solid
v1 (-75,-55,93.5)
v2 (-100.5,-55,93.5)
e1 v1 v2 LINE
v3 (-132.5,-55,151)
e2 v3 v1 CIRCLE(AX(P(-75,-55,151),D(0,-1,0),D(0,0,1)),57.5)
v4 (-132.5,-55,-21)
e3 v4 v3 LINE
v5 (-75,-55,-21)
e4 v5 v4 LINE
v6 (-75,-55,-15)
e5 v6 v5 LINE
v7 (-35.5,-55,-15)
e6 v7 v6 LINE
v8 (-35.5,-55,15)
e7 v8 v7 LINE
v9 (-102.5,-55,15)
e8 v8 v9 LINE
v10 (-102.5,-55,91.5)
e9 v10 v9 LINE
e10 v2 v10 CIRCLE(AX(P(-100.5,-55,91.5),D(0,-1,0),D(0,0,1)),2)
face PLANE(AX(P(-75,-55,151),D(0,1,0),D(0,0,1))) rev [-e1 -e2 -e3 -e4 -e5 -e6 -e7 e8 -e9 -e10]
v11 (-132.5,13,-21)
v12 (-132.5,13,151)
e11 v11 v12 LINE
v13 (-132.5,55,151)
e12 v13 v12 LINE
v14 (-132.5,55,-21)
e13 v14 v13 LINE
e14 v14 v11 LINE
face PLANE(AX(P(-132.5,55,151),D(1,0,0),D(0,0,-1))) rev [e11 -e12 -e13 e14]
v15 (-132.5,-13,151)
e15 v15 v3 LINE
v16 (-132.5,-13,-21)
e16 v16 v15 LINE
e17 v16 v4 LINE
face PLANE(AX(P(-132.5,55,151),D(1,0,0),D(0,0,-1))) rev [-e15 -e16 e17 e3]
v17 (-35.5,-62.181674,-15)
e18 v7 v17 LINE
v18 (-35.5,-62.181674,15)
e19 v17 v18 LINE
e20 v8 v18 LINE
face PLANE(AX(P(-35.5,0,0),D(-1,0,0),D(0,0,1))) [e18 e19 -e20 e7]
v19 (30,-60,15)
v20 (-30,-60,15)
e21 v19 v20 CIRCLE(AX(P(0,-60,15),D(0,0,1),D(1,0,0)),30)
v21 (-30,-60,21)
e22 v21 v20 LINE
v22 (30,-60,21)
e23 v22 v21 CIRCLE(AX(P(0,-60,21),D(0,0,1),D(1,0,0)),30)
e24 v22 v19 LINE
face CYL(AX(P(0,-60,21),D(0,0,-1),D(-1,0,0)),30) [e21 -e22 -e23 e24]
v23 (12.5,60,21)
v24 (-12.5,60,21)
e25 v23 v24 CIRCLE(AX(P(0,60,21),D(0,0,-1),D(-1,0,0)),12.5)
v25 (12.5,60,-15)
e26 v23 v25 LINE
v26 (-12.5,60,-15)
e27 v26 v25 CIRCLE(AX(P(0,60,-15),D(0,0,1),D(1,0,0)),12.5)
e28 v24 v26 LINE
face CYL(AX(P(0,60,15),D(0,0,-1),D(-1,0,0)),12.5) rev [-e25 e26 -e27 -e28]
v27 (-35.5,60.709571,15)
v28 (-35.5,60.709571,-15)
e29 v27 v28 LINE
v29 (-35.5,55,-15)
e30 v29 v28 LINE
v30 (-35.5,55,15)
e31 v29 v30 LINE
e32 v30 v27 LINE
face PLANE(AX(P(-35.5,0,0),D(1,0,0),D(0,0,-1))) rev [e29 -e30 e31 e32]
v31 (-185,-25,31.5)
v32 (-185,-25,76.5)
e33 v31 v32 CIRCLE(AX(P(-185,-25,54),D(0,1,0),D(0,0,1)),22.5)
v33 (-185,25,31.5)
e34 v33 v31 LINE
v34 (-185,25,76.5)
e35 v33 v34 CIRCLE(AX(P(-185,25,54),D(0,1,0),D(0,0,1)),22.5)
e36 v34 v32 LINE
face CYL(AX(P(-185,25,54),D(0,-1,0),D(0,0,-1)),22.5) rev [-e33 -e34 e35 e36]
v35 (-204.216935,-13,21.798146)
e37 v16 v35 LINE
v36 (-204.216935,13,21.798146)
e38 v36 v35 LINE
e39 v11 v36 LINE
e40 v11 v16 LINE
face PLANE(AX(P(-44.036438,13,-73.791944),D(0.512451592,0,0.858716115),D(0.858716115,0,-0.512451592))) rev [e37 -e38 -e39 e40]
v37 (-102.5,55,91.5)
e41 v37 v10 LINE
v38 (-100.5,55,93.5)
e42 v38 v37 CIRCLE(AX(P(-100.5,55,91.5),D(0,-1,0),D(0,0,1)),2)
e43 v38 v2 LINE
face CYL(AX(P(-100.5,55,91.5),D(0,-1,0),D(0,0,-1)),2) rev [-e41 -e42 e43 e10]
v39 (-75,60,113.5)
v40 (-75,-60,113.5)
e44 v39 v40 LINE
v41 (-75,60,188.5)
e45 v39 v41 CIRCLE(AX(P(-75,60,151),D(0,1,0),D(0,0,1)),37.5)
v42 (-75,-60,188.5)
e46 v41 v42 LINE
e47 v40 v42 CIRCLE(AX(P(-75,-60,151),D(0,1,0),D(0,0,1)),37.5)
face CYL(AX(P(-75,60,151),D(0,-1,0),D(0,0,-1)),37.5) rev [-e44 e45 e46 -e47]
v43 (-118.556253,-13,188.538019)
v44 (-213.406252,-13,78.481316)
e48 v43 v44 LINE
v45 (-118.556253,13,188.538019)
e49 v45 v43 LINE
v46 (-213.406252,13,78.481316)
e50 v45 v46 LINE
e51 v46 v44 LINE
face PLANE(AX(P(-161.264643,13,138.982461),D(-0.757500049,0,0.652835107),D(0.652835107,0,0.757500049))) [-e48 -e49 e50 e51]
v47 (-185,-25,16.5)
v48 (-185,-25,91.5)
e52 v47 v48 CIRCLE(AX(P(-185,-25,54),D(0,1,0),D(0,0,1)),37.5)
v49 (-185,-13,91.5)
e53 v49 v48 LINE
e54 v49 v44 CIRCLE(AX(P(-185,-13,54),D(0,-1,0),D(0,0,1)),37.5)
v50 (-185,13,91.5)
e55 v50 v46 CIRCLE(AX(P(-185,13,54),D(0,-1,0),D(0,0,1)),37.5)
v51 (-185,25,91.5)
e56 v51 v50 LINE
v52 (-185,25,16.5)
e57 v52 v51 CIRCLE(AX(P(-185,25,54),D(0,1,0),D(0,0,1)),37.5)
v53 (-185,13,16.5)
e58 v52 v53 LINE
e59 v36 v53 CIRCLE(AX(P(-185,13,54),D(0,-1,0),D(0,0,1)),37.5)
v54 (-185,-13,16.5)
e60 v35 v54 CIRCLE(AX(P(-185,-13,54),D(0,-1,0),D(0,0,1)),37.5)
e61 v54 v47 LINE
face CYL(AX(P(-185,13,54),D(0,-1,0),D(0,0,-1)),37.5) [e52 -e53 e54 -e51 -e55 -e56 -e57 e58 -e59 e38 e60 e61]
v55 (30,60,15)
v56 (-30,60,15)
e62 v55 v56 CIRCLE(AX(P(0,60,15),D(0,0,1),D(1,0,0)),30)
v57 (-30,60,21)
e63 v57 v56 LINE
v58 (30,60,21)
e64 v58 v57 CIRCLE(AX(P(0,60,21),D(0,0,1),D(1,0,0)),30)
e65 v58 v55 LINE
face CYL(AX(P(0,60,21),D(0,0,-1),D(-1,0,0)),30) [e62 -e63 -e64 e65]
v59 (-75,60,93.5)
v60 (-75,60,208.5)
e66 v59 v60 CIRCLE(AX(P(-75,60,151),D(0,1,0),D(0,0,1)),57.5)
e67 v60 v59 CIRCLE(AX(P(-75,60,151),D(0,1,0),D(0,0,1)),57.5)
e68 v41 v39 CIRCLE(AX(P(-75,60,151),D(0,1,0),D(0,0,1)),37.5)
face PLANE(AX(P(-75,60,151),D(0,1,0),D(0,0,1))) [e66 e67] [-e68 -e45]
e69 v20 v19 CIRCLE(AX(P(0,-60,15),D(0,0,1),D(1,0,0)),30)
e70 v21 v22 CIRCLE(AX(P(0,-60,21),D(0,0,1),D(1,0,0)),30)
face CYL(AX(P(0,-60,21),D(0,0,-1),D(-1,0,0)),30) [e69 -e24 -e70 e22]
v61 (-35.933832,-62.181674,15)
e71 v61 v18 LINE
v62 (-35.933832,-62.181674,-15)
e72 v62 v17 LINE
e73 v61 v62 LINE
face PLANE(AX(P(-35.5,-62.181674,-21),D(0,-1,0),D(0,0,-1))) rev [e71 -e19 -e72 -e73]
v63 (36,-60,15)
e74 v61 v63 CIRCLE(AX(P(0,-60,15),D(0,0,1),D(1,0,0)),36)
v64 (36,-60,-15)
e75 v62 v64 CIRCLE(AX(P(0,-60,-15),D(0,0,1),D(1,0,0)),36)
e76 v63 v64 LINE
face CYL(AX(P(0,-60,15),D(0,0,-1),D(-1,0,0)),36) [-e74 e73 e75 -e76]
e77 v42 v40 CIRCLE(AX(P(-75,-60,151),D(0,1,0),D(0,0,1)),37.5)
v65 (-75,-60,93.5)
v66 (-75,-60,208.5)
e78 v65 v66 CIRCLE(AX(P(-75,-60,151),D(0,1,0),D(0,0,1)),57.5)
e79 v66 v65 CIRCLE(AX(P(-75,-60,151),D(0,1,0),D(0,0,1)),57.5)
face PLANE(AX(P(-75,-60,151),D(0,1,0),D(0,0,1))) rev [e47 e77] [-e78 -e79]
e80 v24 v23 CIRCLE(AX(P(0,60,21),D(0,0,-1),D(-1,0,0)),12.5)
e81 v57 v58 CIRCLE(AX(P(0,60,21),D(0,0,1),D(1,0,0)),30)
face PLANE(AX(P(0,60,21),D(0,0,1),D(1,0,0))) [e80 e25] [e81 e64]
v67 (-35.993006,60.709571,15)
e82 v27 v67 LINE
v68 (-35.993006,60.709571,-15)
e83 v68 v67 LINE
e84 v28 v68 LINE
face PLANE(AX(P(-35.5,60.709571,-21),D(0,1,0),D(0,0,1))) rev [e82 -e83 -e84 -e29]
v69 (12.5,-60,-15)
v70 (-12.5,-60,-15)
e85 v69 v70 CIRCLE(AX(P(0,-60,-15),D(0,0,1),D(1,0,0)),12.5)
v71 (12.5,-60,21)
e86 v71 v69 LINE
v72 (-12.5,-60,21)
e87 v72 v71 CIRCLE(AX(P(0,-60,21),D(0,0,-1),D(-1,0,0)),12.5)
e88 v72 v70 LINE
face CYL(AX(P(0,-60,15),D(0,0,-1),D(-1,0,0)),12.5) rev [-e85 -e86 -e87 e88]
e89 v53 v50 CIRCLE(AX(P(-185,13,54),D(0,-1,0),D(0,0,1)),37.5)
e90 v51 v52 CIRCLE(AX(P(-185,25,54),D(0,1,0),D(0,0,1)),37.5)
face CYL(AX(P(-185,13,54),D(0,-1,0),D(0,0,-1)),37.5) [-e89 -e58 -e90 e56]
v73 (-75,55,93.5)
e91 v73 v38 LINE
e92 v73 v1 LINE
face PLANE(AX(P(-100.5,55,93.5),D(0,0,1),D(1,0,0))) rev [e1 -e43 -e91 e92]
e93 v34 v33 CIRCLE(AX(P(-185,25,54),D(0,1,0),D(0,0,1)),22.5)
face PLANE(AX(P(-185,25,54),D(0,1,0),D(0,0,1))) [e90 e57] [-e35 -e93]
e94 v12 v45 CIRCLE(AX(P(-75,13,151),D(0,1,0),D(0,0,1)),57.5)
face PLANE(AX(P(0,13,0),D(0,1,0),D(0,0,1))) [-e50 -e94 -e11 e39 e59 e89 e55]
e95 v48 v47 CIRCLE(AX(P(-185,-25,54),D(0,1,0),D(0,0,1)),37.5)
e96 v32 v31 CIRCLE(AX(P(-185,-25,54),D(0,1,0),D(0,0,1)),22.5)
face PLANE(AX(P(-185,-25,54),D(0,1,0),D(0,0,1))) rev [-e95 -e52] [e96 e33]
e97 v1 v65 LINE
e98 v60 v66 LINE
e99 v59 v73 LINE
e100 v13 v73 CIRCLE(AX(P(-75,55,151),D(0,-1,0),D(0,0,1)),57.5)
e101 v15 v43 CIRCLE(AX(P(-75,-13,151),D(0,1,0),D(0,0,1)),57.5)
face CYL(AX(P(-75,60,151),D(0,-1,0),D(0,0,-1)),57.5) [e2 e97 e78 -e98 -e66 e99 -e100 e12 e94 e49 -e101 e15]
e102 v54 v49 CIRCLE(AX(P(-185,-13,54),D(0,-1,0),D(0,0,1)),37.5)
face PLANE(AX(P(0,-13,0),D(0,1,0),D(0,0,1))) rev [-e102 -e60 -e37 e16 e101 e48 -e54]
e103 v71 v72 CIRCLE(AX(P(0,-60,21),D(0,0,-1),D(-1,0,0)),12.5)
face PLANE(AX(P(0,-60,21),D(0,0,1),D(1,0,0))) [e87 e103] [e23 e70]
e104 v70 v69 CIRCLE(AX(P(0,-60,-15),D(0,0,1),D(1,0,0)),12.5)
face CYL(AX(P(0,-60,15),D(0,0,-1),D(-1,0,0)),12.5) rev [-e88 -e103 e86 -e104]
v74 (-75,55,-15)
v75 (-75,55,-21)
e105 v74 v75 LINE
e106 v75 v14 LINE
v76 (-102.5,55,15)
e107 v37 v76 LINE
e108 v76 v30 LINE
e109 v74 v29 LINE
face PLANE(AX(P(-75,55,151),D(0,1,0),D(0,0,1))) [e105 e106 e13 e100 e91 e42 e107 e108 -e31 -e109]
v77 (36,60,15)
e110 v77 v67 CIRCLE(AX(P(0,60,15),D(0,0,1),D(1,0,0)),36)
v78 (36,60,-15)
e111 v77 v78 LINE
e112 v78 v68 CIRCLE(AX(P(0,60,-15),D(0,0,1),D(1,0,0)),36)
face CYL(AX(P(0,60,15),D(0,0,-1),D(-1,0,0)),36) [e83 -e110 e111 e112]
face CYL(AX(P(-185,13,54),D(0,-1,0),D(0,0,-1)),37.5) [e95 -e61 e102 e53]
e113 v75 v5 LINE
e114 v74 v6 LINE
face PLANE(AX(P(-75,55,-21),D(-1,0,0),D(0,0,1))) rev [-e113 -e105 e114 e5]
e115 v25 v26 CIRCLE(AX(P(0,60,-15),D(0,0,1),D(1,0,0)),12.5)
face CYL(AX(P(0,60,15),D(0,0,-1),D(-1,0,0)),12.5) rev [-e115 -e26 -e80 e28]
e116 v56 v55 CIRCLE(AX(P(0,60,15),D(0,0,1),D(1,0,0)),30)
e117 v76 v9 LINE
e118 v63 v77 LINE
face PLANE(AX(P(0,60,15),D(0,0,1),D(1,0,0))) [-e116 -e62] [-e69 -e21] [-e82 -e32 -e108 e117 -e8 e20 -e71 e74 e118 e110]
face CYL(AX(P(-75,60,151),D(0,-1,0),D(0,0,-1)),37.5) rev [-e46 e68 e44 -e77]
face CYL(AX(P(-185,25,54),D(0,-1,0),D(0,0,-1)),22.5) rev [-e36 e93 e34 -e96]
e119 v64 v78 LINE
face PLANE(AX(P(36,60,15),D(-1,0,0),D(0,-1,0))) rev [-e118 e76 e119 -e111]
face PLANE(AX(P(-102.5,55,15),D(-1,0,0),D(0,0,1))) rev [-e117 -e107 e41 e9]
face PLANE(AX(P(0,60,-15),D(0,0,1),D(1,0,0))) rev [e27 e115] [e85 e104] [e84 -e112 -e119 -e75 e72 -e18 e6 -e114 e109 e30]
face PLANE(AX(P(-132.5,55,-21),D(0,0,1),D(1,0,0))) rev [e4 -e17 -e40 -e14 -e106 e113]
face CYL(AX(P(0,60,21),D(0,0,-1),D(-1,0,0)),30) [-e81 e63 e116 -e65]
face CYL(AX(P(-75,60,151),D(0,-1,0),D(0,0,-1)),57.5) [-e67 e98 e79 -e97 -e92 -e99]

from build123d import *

# Parameters (mm, degrees)
BASE_PROFILE_SKETCH_R     = 12.5
BASE_BODY_DEPTH           = 15
BOSS_PAD_SKETCH_R         = 30
BOSS_PAD_6MM_DEPTH        = 6
BORE_SKETCH_R             = 12.5
BORE_CUT_DEPTH            = 145.976722269
ARM_BLOCK_SKETCH_R        = 57.5
ARM_BLOCK_SKETCH_R_2      = 37.5
ARM_BLOCK_DEPTH           = 60
WEB_DEPTH                 = 55
WEB_POCKET_SKETCH_W       = 39.351063387
WEB_POCKET_SKETCH_H       = 7.1816736
WEB_POCKET_SKETCH_W_2     = 45.776165888
WEB_POCKET_SKETCH_H_2     = 5.709571084
WEB_POCKET_CUT_DEPTH      = 97
MOUNTING_PLATE_SKETCH_R   = 37.5
MOUNTING_PLATE_SKETCH_R_2 = 22.5
MOUNTING_PLATE_DEPTH      = 25
LUG_BOSSES_DEPTH          = 13
LUG_HOLES_SKETCH_R        = 22.5
LUG_HOLES_CUT_DEPTH       = 329.05411139


with BuildPart() as part:
    # Base Profile Sketch → Base Body (new, symmetric)
    with BuildSketch(Plane.XY):
        with BuildLine():
            Line((-36, -60), (-102.5, -60))
            Line((-102.5, -60), (-102.5, 60))
            Line((-102.5, 60), (-36, 60))
            ThreePointArc((-36, 60), (0, 96), (36, 60))
            Line((36, 60), (36, -60))
            ThreePointArc((36, -60), (0, -96), (-36, -60))
        make_face()
        with Locations((0, 60)):
            Circle(BASE_PROFILE_SKETCH_R, mode=Mode.SUBTRACT)
        with Locations((0, -60)):
            Circle(BASE_PROFILE_SKETCH_R, mode=Mode.SUBTRACT)
    extrude(amount=BASE_BODY_DEPTH, both=True)

    # Boss Pad Sketch → Boss Pad 6mm (add)
    with BuildSketch(Plane.XY.offset(15)):
        with Locations((0, -60)):
            Circle(BOSS_PAD_SKETCH_R)
        with Locations((0, 60)):
            Circle(BOSS_PAD_SKETCH_R)
    extrude(amount=BOSS_PAD_6MM_DEPTH)

    # Bore Sketch → Bore Cut (cut, through all)
    with BuildSketch(Plane(origin=(0, 0, -15), x_dir=(-1, 0, 0), z_dir=(0, 0, -1))):
        with Locations((0, -60)):
            Circle(BORE_SKETCH_R)
        with Locations((0, 60)):
            Circle(BORE_SKETCH_R)
    extrude(amount=-BORE_CUT_DEPTH, mode=Mode.SUBTRACT)



with BuildPart() as body_2:
    # Arm Block Sketch → Arm Block (new, symmetric)
    with BuildSketch(Plane(origin=(0, 0, 0), x_dir=(1, 0, 0), z_dir=(0, 1, 0))):
        with Locations(Location((-75, -151, 0), (0, 0, 270))):
            Circle(ARM_BLOCK_SKETCH_R)
        with Locations(Location((-75, -151, 0), (0, 0, 270))):
            Circle(ARM_BLOCK_SKETCH_R_2, mode=Mode.SUBTRACT)
    extrude(amount=ARM_BLOCK_DEPTH, both=True)


with BuildPart() as part_1:
    add(part.part)

    add(body_2.part)  # Web merges body 2
    # Web Profile Sketch → Web (add, symmetric)
    with BuildSketch(Plane(origin=(0, 0, 0), x_dir=(1, 0, 0), z_dir=(0, 1, 0))):
        with BuildLine():
            Line((-132.5, -151), (-132.5, 21))
            Line((-132.5, 21), (-75, 21))
            Line((-75, 21), (-75, 15))
            Line((-75, 15), (-36, 15))
            Line((-36, 15), (-36, -15))
            Line((-36, -15), (-102.5, -15))
            Line((-102.5, -15), (-102.5, -91.5))
            ThreePointArc((-102.5, -91.5), (-101.914213562, -92.914213562), (-100.5, -93.5))
            Line((-100.5, -93.5), (-75, -93.5))
            ThreePointArc((-75, -93.5), (-115.658639918, -110.341360082), (-132.5, -151))
        make_face()
    extrude(amount=WEB_DEPTH, both=True)

    # Web Pocket Sketch → Web Pocket Cut (cut)
    with BuildSketch(Plane.ZY.offset(132.5)):
        with Locations((-1.324468307, -58.5908368)):
            Rectangle(WEB_POCKET_SKETCH_W, WEB_POCKET_SKETCH_H)
        with Locations((1.888082944, 57.854785542)):
            Rectangle(WEB_POCKET_SKETCH_W_2, WEB_POCKET_SKETCH_H_2)
    extrude(amount=-WEB_POCKET_CUT_DEPTH, mode=Mode.SUBTRACT)



with BuildPart() as body_2_2:
    # Mounting Plate Sketch → Mounting Plate (new, symmetric)
    with BuildSketch(Plane(origin=(0, 0, 0), x_dir=(1, 0, 0), z_dir=(0, 1, 0))):
        with Locations(Location((-185, -54, 0), (0, 0, 270))):
            Circle(MOUNTING_PLATE_SKETCH_R)
        with Locations(Location((-185, -54, 0), (0, 0, 270))):
            Circle(MOUNTING_PLATE_SKETCH_R_2, mode=Mode.SUBTRACT)
    extrude(amount=MOUNTING_PLATE_DEPTH, both=True)


with BuildPart() as part_2:
    add(part_1.part)

    add(body_2_2.part)  # Lug Bosses merges body 2 2
    # Lug Bosses Sketch → Lug Bosses (add, symmetric)
    with BuildSketch(Plane(origin=(0, 0, 0), x_dir=(1, 0, 0), z_dir=(0, 1, 0))):
        with BuildLine():
            Line((-132.5, 21), (-204.216934712, -21.798145701))
            ThreePointArc((-204.216934712, -21.798145701), (-222.016718342, -47.998953157), (-213.406251821, -78.481316498))
            Line((-213.406251821, -78.481316498), (-118.556252792, -188.53801863))
            Line((-118.556252792, -188.53801863), (-118.556252792, 21))
            Line((-118.556252792, 21), (-132.5, 21))
        make_face()
    extrude(amount=LUG_BOSSES_DEPTH, both=True)

    # Lug Holes Sketch → Lug Holes Cut (cut, through all)
    with BuildSketch(Plane.XZ.offset(25)):
        with Locations(Location((-185, 54, 0), (0, 0, 90))):
            Circle(LUG_HOLES_SKETCH_R)
    extrude(amount=-LUG_HOLES_CUT_DEPTH, mode=Mode.SUBTRACT)


solid = part_2.part
